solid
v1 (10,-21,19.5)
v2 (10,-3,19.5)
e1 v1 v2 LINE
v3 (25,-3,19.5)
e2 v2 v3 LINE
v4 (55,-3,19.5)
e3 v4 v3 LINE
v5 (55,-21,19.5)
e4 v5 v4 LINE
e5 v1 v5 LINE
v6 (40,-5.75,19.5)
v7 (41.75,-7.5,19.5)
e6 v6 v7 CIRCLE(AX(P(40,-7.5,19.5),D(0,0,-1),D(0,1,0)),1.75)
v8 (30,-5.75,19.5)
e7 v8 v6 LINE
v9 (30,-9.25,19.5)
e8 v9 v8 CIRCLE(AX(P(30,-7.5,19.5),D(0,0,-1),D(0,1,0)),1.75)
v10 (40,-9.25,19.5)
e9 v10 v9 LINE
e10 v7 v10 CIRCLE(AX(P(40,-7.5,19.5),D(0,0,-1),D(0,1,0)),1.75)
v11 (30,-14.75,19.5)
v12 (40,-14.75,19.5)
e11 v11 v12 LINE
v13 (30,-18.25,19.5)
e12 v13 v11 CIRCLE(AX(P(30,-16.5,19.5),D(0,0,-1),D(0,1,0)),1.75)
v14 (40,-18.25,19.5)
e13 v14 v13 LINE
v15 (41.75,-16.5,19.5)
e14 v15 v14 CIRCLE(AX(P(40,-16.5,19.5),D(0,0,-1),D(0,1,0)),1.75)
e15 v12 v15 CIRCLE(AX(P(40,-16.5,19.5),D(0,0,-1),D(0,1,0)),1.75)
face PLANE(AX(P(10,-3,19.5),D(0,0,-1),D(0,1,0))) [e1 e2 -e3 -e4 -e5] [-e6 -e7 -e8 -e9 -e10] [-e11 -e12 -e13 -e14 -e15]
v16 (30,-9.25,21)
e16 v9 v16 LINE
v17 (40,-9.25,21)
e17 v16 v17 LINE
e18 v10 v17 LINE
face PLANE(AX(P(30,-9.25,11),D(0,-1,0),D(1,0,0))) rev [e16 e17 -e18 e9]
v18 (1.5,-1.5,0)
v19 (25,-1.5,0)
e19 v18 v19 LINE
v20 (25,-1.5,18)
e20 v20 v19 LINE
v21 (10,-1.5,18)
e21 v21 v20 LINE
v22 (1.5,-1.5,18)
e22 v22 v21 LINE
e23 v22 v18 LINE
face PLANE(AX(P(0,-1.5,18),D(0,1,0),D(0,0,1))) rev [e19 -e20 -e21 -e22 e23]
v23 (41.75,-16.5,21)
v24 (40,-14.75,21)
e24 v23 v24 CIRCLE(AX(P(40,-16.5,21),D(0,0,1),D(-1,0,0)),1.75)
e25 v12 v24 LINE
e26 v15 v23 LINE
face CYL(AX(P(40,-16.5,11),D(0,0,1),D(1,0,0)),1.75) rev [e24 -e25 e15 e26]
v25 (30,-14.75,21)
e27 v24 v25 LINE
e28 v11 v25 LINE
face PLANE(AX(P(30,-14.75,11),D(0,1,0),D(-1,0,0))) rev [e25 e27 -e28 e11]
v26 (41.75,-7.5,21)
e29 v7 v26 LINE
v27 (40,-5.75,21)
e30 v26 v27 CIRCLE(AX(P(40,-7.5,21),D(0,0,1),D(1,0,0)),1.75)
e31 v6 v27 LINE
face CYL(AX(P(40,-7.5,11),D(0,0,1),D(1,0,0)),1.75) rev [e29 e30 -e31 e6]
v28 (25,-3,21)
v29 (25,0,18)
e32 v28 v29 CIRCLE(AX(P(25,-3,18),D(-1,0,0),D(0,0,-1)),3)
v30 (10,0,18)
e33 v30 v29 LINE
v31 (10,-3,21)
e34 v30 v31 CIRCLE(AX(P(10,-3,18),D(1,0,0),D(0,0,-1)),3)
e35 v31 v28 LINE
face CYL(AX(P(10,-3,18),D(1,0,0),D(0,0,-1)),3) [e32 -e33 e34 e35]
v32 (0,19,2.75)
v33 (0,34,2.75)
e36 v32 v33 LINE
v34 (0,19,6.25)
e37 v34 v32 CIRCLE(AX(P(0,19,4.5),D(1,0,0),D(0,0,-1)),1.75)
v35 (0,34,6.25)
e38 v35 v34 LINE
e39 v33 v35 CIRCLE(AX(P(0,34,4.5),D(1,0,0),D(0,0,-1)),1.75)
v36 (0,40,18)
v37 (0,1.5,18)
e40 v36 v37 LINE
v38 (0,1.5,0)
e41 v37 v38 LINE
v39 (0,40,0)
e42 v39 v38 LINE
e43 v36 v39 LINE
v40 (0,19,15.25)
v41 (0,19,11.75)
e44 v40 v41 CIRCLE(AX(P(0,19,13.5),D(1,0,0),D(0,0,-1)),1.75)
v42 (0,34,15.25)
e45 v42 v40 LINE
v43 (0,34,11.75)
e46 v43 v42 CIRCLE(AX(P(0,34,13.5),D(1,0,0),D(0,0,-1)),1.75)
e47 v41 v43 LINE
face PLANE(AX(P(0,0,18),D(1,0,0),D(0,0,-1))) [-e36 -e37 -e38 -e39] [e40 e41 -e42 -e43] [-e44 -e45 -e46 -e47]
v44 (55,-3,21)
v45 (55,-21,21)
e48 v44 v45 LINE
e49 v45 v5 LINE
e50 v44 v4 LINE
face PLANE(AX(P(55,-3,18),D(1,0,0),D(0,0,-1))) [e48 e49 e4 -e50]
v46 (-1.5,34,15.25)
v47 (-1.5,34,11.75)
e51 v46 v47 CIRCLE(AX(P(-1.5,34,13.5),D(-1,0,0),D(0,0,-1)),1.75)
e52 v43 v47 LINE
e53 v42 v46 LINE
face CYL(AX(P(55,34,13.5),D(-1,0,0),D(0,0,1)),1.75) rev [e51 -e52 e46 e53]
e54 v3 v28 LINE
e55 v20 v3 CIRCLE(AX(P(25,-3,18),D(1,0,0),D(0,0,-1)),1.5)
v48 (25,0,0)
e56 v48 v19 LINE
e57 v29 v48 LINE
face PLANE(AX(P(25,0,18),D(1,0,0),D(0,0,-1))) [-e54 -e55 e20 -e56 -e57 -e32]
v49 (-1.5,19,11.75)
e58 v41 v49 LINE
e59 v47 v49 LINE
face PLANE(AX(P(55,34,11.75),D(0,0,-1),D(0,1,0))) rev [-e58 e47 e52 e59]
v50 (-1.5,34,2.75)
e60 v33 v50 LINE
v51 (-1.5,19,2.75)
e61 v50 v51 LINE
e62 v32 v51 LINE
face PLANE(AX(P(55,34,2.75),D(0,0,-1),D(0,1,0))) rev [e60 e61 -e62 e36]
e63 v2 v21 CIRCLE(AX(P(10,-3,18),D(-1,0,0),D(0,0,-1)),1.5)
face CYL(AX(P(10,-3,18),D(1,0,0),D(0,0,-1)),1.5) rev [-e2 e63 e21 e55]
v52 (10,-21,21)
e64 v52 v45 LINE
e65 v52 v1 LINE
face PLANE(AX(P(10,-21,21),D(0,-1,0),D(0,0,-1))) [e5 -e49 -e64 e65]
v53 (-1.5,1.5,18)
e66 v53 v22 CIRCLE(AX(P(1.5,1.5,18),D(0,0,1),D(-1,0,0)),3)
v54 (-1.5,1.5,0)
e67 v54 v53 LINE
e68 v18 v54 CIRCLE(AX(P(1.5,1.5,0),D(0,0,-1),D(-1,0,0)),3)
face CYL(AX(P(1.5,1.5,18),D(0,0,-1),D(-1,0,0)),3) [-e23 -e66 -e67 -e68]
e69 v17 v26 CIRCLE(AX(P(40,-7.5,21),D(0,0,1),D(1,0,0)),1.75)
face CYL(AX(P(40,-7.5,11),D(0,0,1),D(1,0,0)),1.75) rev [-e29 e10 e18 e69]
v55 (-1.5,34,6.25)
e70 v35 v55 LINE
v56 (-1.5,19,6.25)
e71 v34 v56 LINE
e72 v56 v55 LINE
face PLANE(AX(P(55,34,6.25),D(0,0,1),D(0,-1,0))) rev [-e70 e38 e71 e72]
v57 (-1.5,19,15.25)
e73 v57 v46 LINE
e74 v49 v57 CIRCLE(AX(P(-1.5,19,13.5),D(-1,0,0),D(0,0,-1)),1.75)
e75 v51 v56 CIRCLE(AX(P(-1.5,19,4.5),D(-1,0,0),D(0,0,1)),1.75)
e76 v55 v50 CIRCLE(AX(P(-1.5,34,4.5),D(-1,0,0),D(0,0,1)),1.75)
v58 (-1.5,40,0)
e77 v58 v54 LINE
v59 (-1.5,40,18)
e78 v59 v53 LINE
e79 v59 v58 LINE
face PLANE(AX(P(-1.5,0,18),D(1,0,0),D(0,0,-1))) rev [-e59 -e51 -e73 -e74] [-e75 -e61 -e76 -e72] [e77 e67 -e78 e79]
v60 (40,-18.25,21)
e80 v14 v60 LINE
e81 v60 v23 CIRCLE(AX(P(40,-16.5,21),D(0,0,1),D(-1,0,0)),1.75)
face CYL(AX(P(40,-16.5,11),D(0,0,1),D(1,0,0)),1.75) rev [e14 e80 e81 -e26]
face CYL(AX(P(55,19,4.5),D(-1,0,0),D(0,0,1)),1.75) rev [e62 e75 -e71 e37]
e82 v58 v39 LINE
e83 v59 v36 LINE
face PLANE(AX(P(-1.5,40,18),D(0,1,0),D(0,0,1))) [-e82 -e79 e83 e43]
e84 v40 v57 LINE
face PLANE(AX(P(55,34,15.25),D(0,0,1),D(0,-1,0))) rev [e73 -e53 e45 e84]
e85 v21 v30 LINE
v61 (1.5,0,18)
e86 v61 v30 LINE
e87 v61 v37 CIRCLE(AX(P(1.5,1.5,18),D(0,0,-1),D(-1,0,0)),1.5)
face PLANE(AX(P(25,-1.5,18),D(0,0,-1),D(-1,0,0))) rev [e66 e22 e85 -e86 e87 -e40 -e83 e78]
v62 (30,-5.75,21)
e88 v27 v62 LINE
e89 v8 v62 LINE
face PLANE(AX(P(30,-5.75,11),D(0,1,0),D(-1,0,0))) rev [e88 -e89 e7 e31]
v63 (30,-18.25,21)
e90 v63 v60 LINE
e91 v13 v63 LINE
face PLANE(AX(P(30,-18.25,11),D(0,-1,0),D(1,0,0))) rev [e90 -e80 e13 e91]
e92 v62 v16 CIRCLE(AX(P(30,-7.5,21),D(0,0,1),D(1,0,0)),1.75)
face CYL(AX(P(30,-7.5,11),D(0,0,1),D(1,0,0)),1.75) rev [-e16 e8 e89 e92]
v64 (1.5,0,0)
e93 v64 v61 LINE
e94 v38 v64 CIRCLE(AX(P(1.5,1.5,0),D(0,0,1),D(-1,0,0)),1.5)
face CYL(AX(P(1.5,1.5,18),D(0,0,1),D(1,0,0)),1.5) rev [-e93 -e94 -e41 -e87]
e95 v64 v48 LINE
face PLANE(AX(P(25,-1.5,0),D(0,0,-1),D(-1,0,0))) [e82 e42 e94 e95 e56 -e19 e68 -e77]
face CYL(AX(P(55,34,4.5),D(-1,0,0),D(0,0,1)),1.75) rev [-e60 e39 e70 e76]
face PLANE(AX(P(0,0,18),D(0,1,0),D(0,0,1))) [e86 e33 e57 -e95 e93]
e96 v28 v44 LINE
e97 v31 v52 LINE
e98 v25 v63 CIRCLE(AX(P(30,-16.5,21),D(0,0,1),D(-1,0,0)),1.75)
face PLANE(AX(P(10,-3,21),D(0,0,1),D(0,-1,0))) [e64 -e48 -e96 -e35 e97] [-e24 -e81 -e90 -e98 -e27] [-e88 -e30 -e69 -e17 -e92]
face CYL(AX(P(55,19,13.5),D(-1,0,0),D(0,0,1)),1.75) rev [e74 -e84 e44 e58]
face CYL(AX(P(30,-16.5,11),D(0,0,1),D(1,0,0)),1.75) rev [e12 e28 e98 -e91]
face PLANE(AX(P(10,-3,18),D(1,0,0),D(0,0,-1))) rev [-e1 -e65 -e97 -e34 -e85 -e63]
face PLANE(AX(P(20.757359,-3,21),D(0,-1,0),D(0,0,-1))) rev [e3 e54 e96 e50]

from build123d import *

# Parameters (mm, degrees)
EXTRUDE_THIN1_DEPTH      = 18
FILLET2_R                = 1.5
FILLET3_R                = 3
BOSS_EXTRUDE1_DEPTH      = 30
BOSS_EXTRUDE1_DEPTH_BACK = 15
SKETCH5_W                = 3
SKETCH5_H                = 3
CUT_EXTRUDE2_DEPTH       = 30
CUT_EXTRUDE3_DEPTH       = 73.341205409
CUT_EXTRUDE4_DEPTH       = 10


with BuildPart() as part:
    # Sketch1 → Extrude-Thin1 (new body)
    with BuildSketch(Plane.XY):
        Polygon((25, 0), (0, 0), (0, 40), (-1.5, 40), (-1.5, -1.5), (25, -1.5), align=None)
    extrude(amount=EXTRUDE_THIN1_DEPTH)

    # Fillet2
    fillet2_edges = [part.edges().sort_by_distance(p)[0] for p in [
        (0, 0, 9),
    ]]
    fillet(fillet2_edges, radius=FILLET2_R)

    # Fillet3
    fillet3_edges = [part.edges().sort_by_distance(p)[0] for p in [
        (-1.5, -1.5, 9),
    ]]
    fillet(fillet3_edges, radius=FILLET3_R)

    # Sketch4 → Boss-Extrude1 (add, two sides: drawn at the far end of the back side and taken through both)
    with BuildSketch(Plane(origin=(25, 0, 0), x_dir=(0, 0, -1), z_dir=(1, 0, 0)).offset(-BOSS_EXTRUDE1_DEPTH_BACK)):
        with BuildLine():
            Line((-21, -3), (-21, -21))
            Line((-21, -21), (-19.5, -21))
            Line((-19.5, -21), (-19.5, -3))
            ThreePointArc((-19.5, -3), (-19.060660172, -1.939339828), (-18, -1.5))
            Line((-18, -1.5), (-18, 0))
            ThreePointArc((-18, 0), (-20.121320344, -0.878679656), (-21, -3))
        make_face()
    extrude(amount=BOSS_EXTRUDE1_DEPTH + BOSS_EXTRUDE1_DEPTH_BACK)

    # Sketch5 → Cut-Extrude2 (cut)
    with BuildSketch(Plane(origin=(55, 0, 0), x_dir=(0, 0, -1), z_dir=(1, 0, 0))):
        with Locations((-19.5, -1.5)):
            Rectangle(SKETCH5_W, SKETCH5_H)
    extrude(amount=-CUT_EXTRUDE2_DEPTH, mode=Mode.SUBTRACT)

    # Sketch6 → Cut-Extrude3 (cut, through all)
    with BuildSketch(Plane.ZY.offset(1.5)):
        with BuildLine():
            Line((6.25, 34), (6.25, 19))
            ThreePointArc((6.25, 19), (4.5, 17.25), (2.75, 19))
            Line((2.75, 19), (2.75, 34))
            ThreePointArc((2.75, 34), (4.5, 35.75), (6.25, 34))
        make_face()
        with BuildLine():
            Line((11.75, 34), (11.75, 19))
            ThreePointArc((11.75, 19), (13.5, 17.25), (15.25, 19))
            Line((15.25, 19), (15.25, 34))
            ThreePointArc((15.25, 34), (13.5, 35.75), (11.75, 34))
        make_face()
    extrude(amount=-CUT_EXTRUDE3_DEPTH, mode=Mode.SUBTRACT)

    # Sketch7 → Cut-Extrude4 (cut)
    with BuildSketch(Plane.XY.offset(21)):
        with BuildLine():
            Line((30, -5.75), (40, -5.75))
            ThreePointArc((40, -5.75), (41.75, -7.5), (40, -9.25))
            Line((40, -9.25), (30, -9.25))
            ThreePointArc((30, -9.25), (28.25, -7.5), (30, -5.75))
        make_face()
        with BuildLine():
            Line((30, -18.25), (40, -18.25))
            ThreePointArc((40, -18.25), (41.75, -16.5), (40, -14.75))
            Line((40, -14.75), (30, -14.75))
            ThreePointArc((30, -14.75), (28.25, -16.5), (30, -18.25))
        make_face()
    extrude(amount=-CUT_EXTRUDE4_DEPTH, mode=Mode.SUBTRACT)


solid = part.part
